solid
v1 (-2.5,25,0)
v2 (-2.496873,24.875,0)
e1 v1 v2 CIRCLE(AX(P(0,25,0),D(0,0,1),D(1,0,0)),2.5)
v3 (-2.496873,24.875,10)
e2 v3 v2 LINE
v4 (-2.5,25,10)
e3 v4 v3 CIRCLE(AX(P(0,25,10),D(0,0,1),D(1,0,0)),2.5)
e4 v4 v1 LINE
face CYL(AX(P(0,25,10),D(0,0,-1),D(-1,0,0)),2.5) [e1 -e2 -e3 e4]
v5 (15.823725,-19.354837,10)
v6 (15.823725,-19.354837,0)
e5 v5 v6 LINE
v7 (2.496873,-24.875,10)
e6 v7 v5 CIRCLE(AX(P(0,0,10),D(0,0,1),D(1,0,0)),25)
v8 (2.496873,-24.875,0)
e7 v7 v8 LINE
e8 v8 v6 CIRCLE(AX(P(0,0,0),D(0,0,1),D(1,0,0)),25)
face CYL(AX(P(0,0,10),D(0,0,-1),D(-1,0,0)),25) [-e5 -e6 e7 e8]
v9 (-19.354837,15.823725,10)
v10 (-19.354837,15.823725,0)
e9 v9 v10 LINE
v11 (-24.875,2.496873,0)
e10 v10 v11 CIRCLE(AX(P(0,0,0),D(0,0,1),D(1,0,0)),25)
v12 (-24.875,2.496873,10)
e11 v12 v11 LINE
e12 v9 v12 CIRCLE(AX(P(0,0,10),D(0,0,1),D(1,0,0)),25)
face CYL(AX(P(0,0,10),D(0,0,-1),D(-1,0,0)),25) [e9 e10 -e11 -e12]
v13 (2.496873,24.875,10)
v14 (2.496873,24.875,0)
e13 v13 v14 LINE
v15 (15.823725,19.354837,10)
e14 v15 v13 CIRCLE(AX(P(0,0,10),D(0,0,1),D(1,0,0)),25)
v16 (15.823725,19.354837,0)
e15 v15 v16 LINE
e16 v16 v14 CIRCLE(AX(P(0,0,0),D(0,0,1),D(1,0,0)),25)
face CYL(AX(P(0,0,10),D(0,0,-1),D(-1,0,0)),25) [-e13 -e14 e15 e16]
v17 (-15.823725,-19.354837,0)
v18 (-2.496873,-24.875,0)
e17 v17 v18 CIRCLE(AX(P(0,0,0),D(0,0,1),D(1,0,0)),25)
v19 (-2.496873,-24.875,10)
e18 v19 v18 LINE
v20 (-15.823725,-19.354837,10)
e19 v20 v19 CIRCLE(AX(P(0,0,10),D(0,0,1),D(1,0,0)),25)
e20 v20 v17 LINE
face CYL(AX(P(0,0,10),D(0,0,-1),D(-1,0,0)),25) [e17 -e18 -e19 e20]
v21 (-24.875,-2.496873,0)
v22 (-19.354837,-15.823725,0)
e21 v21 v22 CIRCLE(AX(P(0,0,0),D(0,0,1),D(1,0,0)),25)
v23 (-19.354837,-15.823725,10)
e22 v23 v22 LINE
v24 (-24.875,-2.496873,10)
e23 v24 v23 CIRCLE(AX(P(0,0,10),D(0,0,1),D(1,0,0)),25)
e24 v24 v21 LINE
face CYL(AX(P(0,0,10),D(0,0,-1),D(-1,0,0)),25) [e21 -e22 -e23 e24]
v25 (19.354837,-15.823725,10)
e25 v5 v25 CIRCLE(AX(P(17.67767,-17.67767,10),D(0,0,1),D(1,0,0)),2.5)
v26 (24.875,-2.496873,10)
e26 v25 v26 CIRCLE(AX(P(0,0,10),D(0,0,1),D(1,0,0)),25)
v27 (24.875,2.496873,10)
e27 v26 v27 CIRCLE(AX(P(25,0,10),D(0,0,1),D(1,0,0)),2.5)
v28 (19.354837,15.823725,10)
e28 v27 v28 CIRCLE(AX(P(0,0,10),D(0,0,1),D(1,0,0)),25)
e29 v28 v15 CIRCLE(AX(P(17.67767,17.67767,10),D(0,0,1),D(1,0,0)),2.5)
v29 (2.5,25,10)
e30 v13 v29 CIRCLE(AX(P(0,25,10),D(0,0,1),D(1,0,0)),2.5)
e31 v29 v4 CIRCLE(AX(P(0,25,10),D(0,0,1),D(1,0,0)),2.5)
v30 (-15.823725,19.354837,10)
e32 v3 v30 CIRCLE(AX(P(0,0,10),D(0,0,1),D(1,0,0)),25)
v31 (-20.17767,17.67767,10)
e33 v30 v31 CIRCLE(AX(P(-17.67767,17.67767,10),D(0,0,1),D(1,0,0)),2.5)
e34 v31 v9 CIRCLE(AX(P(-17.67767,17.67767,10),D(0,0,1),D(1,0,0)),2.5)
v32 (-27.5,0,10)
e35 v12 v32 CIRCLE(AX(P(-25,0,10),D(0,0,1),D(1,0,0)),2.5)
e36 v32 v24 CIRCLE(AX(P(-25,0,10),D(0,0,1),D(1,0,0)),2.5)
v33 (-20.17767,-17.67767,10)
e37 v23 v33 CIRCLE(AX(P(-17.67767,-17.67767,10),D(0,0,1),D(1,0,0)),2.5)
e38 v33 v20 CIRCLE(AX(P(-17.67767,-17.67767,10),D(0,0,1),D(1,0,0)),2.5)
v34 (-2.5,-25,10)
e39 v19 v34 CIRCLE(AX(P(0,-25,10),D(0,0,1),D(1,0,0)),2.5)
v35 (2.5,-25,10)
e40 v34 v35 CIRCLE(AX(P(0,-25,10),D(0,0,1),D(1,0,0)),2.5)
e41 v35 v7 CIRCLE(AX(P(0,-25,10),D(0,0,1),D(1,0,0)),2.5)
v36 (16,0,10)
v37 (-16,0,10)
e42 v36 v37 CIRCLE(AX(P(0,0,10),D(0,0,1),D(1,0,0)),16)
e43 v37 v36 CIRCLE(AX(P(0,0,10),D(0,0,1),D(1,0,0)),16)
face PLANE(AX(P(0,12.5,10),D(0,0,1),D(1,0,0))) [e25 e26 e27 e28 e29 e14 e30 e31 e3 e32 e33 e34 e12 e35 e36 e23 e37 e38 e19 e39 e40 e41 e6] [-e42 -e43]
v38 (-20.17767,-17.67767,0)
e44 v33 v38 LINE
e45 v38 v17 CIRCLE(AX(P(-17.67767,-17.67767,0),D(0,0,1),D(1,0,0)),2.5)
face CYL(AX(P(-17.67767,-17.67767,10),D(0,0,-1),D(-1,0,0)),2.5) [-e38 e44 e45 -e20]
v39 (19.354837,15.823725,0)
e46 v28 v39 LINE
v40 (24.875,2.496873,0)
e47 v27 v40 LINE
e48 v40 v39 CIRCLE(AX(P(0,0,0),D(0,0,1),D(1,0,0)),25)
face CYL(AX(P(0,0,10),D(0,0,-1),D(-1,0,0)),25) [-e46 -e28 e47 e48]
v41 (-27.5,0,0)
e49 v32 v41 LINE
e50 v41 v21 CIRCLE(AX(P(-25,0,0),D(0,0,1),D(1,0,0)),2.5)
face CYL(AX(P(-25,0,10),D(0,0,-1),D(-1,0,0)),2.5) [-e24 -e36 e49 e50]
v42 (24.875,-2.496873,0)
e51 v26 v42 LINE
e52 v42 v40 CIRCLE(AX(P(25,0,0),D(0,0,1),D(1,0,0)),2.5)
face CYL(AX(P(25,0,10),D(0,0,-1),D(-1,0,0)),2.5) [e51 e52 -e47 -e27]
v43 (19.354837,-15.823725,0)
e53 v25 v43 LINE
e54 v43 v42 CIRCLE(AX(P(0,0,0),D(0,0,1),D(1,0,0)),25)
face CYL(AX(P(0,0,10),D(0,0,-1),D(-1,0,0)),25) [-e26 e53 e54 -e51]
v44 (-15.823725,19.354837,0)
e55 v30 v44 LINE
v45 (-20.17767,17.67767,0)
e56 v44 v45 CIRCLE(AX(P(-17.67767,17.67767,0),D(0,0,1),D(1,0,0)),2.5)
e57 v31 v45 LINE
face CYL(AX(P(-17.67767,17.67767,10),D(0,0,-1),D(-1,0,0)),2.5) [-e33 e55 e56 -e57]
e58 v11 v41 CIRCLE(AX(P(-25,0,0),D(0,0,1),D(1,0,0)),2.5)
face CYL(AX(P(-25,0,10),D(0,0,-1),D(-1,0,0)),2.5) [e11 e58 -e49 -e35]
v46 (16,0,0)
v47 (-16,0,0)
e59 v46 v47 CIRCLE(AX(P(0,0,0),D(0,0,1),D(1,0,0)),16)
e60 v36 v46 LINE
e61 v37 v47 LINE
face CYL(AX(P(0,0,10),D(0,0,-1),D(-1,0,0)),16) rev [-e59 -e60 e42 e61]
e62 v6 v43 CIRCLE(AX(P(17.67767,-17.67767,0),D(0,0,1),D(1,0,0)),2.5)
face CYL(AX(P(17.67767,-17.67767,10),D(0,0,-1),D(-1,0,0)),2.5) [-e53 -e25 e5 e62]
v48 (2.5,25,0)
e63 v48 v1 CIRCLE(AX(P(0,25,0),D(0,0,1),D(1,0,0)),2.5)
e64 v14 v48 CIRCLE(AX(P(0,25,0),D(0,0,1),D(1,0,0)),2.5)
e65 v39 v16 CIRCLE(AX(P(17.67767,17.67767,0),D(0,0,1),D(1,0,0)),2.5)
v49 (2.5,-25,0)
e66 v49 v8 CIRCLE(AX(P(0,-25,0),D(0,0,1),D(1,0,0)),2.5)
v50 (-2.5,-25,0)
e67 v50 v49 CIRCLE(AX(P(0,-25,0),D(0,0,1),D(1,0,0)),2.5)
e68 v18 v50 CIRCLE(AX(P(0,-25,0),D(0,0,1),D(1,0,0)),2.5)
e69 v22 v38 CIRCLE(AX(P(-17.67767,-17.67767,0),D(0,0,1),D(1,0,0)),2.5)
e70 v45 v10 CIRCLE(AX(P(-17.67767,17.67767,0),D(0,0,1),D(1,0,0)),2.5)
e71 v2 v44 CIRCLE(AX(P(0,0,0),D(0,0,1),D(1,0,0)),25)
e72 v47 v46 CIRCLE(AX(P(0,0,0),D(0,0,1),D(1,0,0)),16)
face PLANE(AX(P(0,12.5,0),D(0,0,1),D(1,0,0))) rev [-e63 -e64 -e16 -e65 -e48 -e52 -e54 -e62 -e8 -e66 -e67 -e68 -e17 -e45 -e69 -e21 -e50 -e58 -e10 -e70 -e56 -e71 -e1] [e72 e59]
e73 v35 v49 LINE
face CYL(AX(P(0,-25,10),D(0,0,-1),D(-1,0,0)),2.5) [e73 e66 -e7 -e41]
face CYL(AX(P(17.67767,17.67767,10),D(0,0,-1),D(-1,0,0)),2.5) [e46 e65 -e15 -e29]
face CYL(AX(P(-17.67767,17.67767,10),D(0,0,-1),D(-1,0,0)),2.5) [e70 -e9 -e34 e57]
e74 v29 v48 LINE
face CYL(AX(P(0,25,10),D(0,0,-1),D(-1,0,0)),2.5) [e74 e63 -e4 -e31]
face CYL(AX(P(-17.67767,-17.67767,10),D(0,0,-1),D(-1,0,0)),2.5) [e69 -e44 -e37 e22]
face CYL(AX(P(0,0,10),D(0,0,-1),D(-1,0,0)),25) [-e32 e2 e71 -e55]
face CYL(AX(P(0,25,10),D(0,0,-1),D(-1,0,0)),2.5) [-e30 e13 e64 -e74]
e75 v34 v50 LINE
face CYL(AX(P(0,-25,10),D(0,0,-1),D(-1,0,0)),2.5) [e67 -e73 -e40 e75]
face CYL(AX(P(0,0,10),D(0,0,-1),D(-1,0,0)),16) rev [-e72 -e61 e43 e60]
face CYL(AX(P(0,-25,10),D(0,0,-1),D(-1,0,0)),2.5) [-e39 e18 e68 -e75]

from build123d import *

# Parameters (mm, degrees)
SKETCH_1_R      = 16
EXTRUDE_1_DEPTH = 10


with BuildPart() as part:
    # 草图1 → 凸台-拉伸1 (new body)
    with BuildSketch(Plane.XY):
        with BuildLine():
            ThreePointArc((-2.496873044, 24.875), (-9.567085809, 23.096988313), (-15.823725321, 19.354837043))
            ThreePointArc((-15.823725321, 19.354837043), (-19.445436483, 19.445436483), (-19.354837043, 15.823725321))
            ThreePointArc((-19.354837043, 15.823725321), (-23.096988313, 9.567085809), (-24.875, 2.496873044))
            ThreePointArc((-24.875, 2.496873044), (-27.5, 0), (-24.875, -2.496873044))
            ThreePointArc((-24.875, -2.496873044), (-23.096988313, -9.567085809), (-19.354837043, -15.823725321))
            ThreePointArc((-19.354837043, -15.823725321), (-19.445436483, -19.445436483), (-15.823725321, -19.354837043))
            ThreePointArc((-15.823725321, -19.354837043), (-9.567085809, -23.096988313), (-2.496873044, -24.875))
            ThreePointArc((-2.496873044, -24.875), (0, -27.5), (2.496873044, -24.875))
            ThreePointArc((2.496873044, -24.875), (9.567085809, -23.096988313), (15.823725321, -19.354837043))
            ThreePointArc((15.823725321, -19.354837043), (19.445436483, -19.445436483), (19.354837043, -15.823725321))
            ThreePointArc((19.354837043, -15.823725321), (23.096988313, -9.567085809), (24.875, -2.496873044))
            ThreePointArc((24.875, -2.496873044), (27.5, 0), (24.875, 2.496873044))
            ThreePointArc((24.875, 2.496873044), (23.096988313, 9.567085809), (19.354837043, 15.823725321))
            ThreePointArc((19.354837043, 15.823725321), (19.445436483, 19.445436483), (15.823725321, 19.354837043))
            ThreePointArc((15.823725321, 19.354837043), (9.567085809, 23.096988313), (2.496873044, 24.875))
            ThreePointArc((2.496873044, 24.875), (0, 27.5), (-2.496873044, 24.875))
        make_face()
        Circle(SKETCH_1_R, mode=Mode.SUBTRACT)
    extrude(amount=EXTRUDE_1_DEPTH)


solid = part.part
